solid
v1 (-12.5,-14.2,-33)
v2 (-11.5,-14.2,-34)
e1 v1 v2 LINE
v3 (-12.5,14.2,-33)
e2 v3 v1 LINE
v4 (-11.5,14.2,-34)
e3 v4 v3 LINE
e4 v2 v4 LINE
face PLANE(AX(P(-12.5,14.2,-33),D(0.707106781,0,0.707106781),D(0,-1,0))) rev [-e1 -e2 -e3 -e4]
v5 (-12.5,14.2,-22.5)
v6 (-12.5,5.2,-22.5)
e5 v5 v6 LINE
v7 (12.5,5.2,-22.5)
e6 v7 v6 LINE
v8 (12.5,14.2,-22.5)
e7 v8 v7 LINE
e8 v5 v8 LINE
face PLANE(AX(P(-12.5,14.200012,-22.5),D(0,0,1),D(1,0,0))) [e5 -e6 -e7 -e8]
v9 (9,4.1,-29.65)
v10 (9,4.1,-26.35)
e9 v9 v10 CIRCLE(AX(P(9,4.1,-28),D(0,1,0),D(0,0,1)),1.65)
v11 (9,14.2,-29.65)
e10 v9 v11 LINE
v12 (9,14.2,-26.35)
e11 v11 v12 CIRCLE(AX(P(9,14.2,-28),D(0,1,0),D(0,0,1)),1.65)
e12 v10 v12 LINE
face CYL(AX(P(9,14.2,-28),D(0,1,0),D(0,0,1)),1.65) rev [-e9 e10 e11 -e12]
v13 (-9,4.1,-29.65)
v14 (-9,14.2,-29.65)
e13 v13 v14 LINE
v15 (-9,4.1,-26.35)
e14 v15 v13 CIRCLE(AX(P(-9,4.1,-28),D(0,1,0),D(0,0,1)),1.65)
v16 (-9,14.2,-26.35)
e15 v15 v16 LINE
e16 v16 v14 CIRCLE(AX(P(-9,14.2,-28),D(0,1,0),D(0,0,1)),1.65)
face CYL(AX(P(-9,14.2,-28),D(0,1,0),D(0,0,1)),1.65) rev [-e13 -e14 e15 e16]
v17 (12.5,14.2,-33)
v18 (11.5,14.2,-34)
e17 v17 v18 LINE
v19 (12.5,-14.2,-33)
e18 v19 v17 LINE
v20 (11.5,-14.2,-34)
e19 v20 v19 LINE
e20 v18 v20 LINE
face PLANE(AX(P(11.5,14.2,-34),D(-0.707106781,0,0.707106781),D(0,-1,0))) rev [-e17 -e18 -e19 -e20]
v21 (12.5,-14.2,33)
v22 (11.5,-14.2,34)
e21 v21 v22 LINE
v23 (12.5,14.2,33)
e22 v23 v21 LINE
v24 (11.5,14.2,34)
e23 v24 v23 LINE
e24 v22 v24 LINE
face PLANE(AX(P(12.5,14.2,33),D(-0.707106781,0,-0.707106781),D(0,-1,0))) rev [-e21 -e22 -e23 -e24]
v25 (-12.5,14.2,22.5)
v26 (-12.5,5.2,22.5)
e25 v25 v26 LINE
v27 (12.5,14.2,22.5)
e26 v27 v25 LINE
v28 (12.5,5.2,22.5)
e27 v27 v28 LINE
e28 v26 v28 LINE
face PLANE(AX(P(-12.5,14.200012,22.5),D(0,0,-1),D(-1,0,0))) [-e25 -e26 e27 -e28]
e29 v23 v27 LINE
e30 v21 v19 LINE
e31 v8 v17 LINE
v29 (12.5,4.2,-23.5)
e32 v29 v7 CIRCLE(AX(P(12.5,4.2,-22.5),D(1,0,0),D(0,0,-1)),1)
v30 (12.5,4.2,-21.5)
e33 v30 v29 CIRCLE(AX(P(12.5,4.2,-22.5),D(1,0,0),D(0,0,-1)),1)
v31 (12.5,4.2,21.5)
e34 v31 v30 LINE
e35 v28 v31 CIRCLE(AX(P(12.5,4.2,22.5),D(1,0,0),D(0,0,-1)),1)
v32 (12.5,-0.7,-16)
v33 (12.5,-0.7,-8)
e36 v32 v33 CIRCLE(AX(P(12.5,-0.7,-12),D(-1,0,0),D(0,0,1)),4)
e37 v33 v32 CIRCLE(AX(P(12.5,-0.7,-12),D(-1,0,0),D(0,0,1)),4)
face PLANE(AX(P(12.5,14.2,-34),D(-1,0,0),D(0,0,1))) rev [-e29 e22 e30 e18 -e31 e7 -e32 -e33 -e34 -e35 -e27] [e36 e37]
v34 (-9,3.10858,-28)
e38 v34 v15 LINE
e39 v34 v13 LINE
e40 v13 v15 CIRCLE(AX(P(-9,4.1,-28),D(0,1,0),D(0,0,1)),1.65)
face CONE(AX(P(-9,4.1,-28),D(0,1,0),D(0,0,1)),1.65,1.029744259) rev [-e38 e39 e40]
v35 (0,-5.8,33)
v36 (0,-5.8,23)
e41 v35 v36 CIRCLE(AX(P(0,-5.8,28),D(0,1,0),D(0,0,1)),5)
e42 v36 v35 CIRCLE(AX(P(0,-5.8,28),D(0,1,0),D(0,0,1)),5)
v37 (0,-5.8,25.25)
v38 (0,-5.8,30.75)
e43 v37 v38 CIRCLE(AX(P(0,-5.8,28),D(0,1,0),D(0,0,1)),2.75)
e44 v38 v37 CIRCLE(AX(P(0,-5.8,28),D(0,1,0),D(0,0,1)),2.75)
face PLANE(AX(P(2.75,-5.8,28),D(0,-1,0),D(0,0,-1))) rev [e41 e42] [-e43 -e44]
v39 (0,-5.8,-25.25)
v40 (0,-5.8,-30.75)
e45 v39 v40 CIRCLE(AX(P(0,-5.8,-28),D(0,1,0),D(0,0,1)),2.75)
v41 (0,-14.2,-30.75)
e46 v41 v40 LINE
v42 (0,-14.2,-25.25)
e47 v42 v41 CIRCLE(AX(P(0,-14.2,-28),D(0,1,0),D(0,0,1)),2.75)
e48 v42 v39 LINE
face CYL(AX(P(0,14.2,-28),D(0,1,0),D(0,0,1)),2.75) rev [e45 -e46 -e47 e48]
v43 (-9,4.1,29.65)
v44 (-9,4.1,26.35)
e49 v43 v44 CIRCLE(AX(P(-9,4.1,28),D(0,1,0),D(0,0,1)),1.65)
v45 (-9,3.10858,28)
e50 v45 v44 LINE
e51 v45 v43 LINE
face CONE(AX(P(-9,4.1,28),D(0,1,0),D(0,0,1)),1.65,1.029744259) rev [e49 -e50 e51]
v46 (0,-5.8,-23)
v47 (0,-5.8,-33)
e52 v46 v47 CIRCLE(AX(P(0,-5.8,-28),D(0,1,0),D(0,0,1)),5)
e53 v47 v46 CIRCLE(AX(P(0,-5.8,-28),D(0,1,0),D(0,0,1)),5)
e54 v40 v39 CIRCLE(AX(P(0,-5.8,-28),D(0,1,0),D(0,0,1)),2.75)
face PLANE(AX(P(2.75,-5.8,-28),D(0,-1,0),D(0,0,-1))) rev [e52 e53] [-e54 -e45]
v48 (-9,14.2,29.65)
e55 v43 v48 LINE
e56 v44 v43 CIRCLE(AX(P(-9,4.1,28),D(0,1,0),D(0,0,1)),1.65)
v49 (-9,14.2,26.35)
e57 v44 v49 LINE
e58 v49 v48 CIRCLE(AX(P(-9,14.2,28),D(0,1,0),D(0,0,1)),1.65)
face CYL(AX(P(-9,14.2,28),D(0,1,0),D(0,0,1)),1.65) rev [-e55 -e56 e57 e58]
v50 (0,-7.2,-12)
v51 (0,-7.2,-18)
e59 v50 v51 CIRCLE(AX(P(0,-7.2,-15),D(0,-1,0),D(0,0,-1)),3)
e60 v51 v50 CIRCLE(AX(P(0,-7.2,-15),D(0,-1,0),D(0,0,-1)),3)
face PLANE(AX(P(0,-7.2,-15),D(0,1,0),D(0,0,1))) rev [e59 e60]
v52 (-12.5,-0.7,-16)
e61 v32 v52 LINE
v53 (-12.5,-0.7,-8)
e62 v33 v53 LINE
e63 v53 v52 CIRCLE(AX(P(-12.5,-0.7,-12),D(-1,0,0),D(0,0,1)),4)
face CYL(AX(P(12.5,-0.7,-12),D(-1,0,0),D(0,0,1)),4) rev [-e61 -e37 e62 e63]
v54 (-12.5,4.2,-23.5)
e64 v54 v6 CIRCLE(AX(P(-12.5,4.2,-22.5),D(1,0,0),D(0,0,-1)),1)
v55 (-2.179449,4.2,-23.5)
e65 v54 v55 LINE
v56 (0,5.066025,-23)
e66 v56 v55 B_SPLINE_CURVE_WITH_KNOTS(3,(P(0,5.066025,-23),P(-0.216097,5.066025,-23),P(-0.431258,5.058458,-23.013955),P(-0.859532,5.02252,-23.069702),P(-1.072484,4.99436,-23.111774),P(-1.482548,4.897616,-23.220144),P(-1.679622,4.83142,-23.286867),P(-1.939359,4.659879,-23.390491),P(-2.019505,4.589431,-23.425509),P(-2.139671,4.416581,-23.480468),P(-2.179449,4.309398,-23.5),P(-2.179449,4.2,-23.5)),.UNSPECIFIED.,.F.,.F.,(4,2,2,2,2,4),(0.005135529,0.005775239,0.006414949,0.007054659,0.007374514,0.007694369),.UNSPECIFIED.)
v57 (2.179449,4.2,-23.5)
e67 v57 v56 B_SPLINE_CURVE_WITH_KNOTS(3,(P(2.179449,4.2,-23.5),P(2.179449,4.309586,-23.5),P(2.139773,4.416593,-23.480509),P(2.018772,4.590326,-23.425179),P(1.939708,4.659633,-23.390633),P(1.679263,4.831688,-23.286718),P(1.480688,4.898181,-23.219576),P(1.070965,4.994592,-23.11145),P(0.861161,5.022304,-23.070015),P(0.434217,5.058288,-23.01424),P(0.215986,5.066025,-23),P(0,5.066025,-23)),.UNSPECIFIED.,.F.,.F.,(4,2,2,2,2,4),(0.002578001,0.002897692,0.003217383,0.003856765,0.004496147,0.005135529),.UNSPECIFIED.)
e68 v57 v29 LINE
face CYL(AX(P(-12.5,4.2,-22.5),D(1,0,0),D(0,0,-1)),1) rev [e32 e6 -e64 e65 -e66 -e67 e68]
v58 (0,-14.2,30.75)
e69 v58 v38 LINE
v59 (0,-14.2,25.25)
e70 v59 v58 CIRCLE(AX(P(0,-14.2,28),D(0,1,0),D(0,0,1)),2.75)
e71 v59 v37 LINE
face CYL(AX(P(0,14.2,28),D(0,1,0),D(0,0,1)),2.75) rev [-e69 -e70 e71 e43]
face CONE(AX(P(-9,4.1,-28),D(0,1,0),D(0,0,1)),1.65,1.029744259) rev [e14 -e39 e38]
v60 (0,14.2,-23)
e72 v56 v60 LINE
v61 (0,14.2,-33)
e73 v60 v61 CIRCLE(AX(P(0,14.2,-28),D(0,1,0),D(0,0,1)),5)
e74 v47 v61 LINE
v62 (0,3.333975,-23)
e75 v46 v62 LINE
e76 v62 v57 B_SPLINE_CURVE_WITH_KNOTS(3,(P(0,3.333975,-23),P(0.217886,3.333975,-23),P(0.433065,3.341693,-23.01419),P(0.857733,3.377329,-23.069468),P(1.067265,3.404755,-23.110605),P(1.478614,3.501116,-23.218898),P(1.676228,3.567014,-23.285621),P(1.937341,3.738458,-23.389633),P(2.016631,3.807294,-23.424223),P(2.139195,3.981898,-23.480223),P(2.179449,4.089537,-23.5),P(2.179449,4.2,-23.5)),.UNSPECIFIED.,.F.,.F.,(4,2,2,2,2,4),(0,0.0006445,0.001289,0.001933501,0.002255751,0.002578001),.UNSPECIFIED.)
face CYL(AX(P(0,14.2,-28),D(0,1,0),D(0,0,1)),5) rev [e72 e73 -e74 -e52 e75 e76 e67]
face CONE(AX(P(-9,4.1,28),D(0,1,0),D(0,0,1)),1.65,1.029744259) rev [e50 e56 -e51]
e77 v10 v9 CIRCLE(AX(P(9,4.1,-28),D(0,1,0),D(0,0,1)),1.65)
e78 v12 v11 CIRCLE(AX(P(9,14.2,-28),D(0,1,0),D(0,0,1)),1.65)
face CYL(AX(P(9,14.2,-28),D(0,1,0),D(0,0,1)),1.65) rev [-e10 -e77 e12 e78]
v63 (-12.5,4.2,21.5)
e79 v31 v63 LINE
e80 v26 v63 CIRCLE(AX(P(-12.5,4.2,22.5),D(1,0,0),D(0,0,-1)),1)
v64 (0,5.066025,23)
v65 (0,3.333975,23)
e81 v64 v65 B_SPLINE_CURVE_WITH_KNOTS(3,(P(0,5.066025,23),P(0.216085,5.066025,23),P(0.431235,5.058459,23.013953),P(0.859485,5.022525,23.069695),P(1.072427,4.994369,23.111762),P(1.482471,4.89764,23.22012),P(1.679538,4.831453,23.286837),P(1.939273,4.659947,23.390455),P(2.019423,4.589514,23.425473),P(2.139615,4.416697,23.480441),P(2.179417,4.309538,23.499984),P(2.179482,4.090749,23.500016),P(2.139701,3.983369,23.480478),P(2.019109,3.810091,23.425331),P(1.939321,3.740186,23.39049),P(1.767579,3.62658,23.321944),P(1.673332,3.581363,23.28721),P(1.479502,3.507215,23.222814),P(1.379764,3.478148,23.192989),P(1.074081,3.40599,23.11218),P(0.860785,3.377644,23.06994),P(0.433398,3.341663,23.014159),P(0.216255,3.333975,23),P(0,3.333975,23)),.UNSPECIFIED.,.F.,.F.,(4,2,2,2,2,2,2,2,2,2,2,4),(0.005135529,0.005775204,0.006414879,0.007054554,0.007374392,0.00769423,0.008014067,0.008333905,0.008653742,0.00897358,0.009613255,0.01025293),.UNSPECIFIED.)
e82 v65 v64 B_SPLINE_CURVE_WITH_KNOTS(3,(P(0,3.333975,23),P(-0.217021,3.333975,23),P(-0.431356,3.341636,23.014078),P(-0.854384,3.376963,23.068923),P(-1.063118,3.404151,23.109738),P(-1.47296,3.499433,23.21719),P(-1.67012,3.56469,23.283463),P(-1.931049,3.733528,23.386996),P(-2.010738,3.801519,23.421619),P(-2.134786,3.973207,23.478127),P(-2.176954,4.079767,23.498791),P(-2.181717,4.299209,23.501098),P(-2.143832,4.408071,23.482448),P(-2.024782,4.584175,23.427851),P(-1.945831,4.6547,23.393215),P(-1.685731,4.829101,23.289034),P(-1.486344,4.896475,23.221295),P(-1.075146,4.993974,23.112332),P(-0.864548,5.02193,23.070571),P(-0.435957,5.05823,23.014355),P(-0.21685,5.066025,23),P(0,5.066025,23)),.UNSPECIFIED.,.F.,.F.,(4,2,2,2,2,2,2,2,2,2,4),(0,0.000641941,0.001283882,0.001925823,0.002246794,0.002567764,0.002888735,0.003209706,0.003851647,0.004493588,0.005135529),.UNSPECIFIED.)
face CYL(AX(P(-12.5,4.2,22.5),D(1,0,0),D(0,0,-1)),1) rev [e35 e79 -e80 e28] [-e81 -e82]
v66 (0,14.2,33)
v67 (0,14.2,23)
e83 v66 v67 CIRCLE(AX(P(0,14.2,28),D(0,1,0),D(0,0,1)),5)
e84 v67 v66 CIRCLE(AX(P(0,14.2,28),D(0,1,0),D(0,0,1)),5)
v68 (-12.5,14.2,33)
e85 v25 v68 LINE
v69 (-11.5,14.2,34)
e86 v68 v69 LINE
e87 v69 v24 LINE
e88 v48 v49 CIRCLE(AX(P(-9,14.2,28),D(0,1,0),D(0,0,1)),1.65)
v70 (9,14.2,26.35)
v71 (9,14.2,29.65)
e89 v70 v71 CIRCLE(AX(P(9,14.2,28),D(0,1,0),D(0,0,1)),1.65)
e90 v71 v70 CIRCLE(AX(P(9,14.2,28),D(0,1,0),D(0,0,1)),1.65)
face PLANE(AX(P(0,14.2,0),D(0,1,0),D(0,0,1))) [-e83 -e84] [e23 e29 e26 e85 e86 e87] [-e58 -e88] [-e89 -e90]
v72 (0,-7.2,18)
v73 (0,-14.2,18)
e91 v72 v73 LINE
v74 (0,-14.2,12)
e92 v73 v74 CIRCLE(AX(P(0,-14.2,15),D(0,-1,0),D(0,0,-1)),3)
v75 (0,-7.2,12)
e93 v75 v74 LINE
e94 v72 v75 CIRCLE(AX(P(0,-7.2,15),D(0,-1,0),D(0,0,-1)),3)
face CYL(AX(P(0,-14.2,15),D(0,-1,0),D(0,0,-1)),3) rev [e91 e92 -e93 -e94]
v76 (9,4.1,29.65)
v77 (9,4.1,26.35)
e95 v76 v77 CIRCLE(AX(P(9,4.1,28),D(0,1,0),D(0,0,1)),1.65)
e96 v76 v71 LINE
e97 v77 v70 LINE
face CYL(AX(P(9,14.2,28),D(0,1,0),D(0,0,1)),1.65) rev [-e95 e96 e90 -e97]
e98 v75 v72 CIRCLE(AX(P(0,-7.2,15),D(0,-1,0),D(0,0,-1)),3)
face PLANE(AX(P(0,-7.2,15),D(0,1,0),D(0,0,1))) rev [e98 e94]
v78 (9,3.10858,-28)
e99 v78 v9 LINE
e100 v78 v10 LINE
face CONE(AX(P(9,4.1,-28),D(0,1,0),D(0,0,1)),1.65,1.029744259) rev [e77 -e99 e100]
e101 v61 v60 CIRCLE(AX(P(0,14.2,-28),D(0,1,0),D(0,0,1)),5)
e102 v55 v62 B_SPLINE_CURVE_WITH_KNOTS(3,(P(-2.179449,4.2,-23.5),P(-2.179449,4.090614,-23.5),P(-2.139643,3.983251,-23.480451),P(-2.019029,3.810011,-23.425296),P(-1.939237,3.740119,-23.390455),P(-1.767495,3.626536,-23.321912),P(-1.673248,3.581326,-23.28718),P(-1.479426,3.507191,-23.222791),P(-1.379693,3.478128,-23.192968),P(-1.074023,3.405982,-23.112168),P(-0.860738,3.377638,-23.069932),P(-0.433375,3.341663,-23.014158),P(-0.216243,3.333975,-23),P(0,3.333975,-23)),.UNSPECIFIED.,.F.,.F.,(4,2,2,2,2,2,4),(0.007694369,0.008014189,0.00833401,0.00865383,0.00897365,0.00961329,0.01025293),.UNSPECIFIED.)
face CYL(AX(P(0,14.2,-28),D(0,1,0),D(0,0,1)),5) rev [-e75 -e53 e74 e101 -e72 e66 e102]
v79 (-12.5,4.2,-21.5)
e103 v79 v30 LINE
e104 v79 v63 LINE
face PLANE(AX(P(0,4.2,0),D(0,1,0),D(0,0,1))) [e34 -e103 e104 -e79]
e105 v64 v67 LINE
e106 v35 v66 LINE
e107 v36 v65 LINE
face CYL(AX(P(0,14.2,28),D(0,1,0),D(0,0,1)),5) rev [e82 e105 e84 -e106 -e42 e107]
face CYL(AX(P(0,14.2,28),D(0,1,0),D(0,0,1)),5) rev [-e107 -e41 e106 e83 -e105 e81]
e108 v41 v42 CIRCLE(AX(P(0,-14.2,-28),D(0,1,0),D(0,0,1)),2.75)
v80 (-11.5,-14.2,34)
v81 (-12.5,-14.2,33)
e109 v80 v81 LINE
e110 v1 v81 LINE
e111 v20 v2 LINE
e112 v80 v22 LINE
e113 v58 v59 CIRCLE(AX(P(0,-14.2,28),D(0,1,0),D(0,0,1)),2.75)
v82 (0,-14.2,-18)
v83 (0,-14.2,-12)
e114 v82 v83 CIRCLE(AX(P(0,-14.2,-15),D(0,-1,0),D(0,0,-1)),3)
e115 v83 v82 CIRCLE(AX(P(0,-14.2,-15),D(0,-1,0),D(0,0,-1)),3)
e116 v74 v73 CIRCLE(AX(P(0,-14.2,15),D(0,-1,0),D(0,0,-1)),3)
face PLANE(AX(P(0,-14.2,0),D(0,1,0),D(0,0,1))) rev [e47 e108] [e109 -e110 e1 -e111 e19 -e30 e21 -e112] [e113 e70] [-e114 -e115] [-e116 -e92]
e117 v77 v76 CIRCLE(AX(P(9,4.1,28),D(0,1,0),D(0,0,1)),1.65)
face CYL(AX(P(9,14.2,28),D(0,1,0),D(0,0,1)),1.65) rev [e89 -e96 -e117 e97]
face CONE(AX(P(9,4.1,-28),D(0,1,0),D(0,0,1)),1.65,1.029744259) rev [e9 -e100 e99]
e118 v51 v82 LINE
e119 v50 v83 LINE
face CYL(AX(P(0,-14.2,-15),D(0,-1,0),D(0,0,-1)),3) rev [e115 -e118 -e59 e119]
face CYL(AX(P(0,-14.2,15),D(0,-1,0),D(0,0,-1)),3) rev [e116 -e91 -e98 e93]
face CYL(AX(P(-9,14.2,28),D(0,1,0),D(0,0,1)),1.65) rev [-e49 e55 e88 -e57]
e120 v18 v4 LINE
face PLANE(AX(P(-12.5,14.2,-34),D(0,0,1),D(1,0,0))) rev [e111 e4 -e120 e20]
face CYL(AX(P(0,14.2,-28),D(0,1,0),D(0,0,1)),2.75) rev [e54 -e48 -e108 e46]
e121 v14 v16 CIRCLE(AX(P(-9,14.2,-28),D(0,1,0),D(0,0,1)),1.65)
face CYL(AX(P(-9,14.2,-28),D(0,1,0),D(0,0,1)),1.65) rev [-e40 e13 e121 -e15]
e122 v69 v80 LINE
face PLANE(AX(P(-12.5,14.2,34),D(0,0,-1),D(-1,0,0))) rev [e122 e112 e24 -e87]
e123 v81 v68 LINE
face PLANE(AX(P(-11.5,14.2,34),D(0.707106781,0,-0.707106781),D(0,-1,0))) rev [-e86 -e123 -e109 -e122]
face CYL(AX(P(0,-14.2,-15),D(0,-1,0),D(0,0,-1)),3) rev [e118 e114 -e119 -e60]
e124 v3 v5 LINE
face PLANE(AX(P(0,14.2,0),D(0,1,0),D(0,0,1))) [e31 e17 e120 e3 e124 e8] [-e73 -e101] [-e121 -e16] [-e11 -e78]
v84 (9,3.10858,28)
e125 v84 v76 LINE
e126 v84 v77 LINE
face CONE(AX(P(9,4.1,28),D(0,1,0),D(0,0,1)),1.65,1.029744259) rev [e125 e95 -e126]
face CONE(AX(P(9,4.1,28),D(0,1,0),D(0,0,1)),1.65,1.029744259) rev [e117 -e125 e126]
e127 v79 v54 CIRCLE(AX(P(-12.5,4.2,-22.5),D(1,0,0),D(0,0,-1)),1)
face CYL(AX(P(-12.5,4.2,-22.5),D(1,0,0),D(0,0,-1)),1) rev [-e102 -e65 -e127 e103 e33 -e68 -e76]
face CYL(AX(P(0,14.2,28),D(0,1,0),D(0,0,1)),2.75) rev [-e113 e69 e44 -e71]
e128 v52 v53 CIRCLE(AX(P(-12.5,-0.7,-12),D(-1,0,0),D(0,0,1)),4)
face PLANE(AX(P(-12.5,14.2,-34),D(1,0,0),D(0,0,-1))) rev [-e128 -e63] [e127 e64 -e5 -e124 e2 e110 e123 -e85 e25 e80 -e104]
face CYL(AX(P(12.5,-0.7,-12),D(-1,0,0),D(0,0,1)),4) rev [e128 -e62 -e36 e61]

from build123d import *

# Parameters (mm, degrees)
SKETCH_1_W                   = 25
SKETCH_1_H                   = 68
EXTRUDE_1_DEPTH              = 14.2
CUT_EXTRUDE_1_DEPTH          = 47.030533345
CUT_EXTRUDE_1_DEPTH_BACK     = 10
SKETCH_2_W                   = 25
SKETCH_2_H                   = 45
F_6_0MM_1_D                  = 6
F_6_0MM_1_DEPTH              = 7
HOLE_WIZARD_M5_1_D           = 5.5
HOLE_WIZARD_M5_1_CBORE_D     = 10
HOLE_WIZARD_M5_1_CBORE_DEPTH = 20
HOLE_WIZARD_M4_1_D           = 3.3
HOLE_WIZARD_M4_1_DEPTH       = 10.1
HOLE_WIZARD_M4_1_TIP         = 0.991420021
CHAMFER_1_SIZE               = 1
SKETCH_9_R                   = 4
CUT_EXTRUDE_2_DEPTH          = 45.526845835
SKETCH_10_R                  = 1
CUT_EXTRUDE_3_DEPTH          = 45.526845835


with BuildPart() as part:
    # 草图1 → 凸台-拉伸1 (new, symmetric)
    with BuildSketch(Plane(origin=(0, 0, 0), x_dir=(1, 0, 0), z_dir=(0, 1, 0))):
        Rectangle(SKETCH_1_W, SKETCH_1_H)
    extrude(amount=EXTRUDE_1_DEPTH, both=True)

    # 草图2 → 切除-拉伸1 (cut, two sides: drawn at the far end of the back side and taken through both)
    with BuildSketch(Plane(origin=(0, 14.2, 0), x_dir=(1, 0, 0), z_dir=(0, 1, 0)).offset(-CUT_EXTRUDE_1_DEPTH_BACK)):
        Rectangle(SKETCH_2_W, SKETCH_2_H)
    extrude(amount=CUT_EXTRUDE_1_DEPTH + CUT_EXTRUDE_1_DEPTH_BACK, mode=Mode.SUBTRACT)

    # Ø6.0mm 暗销孔1
    with Locations(Plane(origin=(0, -14.2, 0), x_dir=(-1, 0, 0), z_dir=(0, -1, 0))):
        with Locations((0, 15), (0, -15)):
            Hole(F_6_0MM_1_D / 2, depth=F_6_0MM_1_DEPTH)

    # M5 六角凹头螺钉的柱形沉头孔1 (through all)
    with Locations(Plane(origin=(0, 14.2, 0), x_dir=(1, 0, 0), z_dir=(0, 1, 0))):
        with Locations((0, 28), (0, -28)):
            CounterBoreHole(HOLE_WIZARD_M5_1_D / 2, HOLE_WIZARD_M5_1_CBORE_D / 2, HOLE_WIZARD_M5_1_CBORE_DEPTH)

    # M4 螺纹孔1
    with Locations(Plane(origin=(0, 14.2, 0), x_dir=(1, 0, 0), z_dir=(0, 1, 0))):
        with Locations((-9, -28), (9, -28), (9, 28), (-9, 28)):
            Hole(HOLE_WIZARD_M4_1_D / 2, depth=HOLE_WIZARD_M4_1_DEPTH)
            with Locations((0, 0, -(HOLE_WIZARD_M4_1_DEPTH + HOLE_WIZARD_M4_1_TIP / 2))):  # 118° drill point
                Cone(0, HOLE_WIZARD_M4_1_D / 2, HOLE_WIZARD_M4_1_TIP, mode=Mode.SUBTRACT)

    # 倒角1
    chamfer_1_edges = [part.edges().sort_by_distance(p)[0] for p in [
        (12.5, 0, 34),
        (-12.5, 0, 34),
        (-12.5, 0, -34),
        (12.5, 0, -34),
    ]]
    chamfer(chamfer_1_edges, length=CHAMFER_1_SIZE)

    # 草图9 → 切除-拉伸2 (cut, through all)
    with BuildSketch(Plane.ZY.offset(12.5)):
        with Locations((-12, -0.7)):
            Circle(SKETCH_9_R)
    extrude(amount=-CUT_EXTRUDE_2_DEPTH, mode=Mode.SUBTRACT)

    # 草图10 → 切除-拉伸3 (cut, through all)
    with BuildSketch(Plane(origin=(12.5, 0, 0), x_dir=(0, 0, -1), z_dir=(1, 0, 0))):
        with Locations((-22.5, 4.2)):
            Circle(SKETCH_10_R)
        with Locations((22.5, 4.2)):
            Circle(SKETCH_10_R)
    extrude(amount=-CUT_EXTRUDE_3_DEPTH, mode=Mode.SUBTRACT)


solid = part.part
